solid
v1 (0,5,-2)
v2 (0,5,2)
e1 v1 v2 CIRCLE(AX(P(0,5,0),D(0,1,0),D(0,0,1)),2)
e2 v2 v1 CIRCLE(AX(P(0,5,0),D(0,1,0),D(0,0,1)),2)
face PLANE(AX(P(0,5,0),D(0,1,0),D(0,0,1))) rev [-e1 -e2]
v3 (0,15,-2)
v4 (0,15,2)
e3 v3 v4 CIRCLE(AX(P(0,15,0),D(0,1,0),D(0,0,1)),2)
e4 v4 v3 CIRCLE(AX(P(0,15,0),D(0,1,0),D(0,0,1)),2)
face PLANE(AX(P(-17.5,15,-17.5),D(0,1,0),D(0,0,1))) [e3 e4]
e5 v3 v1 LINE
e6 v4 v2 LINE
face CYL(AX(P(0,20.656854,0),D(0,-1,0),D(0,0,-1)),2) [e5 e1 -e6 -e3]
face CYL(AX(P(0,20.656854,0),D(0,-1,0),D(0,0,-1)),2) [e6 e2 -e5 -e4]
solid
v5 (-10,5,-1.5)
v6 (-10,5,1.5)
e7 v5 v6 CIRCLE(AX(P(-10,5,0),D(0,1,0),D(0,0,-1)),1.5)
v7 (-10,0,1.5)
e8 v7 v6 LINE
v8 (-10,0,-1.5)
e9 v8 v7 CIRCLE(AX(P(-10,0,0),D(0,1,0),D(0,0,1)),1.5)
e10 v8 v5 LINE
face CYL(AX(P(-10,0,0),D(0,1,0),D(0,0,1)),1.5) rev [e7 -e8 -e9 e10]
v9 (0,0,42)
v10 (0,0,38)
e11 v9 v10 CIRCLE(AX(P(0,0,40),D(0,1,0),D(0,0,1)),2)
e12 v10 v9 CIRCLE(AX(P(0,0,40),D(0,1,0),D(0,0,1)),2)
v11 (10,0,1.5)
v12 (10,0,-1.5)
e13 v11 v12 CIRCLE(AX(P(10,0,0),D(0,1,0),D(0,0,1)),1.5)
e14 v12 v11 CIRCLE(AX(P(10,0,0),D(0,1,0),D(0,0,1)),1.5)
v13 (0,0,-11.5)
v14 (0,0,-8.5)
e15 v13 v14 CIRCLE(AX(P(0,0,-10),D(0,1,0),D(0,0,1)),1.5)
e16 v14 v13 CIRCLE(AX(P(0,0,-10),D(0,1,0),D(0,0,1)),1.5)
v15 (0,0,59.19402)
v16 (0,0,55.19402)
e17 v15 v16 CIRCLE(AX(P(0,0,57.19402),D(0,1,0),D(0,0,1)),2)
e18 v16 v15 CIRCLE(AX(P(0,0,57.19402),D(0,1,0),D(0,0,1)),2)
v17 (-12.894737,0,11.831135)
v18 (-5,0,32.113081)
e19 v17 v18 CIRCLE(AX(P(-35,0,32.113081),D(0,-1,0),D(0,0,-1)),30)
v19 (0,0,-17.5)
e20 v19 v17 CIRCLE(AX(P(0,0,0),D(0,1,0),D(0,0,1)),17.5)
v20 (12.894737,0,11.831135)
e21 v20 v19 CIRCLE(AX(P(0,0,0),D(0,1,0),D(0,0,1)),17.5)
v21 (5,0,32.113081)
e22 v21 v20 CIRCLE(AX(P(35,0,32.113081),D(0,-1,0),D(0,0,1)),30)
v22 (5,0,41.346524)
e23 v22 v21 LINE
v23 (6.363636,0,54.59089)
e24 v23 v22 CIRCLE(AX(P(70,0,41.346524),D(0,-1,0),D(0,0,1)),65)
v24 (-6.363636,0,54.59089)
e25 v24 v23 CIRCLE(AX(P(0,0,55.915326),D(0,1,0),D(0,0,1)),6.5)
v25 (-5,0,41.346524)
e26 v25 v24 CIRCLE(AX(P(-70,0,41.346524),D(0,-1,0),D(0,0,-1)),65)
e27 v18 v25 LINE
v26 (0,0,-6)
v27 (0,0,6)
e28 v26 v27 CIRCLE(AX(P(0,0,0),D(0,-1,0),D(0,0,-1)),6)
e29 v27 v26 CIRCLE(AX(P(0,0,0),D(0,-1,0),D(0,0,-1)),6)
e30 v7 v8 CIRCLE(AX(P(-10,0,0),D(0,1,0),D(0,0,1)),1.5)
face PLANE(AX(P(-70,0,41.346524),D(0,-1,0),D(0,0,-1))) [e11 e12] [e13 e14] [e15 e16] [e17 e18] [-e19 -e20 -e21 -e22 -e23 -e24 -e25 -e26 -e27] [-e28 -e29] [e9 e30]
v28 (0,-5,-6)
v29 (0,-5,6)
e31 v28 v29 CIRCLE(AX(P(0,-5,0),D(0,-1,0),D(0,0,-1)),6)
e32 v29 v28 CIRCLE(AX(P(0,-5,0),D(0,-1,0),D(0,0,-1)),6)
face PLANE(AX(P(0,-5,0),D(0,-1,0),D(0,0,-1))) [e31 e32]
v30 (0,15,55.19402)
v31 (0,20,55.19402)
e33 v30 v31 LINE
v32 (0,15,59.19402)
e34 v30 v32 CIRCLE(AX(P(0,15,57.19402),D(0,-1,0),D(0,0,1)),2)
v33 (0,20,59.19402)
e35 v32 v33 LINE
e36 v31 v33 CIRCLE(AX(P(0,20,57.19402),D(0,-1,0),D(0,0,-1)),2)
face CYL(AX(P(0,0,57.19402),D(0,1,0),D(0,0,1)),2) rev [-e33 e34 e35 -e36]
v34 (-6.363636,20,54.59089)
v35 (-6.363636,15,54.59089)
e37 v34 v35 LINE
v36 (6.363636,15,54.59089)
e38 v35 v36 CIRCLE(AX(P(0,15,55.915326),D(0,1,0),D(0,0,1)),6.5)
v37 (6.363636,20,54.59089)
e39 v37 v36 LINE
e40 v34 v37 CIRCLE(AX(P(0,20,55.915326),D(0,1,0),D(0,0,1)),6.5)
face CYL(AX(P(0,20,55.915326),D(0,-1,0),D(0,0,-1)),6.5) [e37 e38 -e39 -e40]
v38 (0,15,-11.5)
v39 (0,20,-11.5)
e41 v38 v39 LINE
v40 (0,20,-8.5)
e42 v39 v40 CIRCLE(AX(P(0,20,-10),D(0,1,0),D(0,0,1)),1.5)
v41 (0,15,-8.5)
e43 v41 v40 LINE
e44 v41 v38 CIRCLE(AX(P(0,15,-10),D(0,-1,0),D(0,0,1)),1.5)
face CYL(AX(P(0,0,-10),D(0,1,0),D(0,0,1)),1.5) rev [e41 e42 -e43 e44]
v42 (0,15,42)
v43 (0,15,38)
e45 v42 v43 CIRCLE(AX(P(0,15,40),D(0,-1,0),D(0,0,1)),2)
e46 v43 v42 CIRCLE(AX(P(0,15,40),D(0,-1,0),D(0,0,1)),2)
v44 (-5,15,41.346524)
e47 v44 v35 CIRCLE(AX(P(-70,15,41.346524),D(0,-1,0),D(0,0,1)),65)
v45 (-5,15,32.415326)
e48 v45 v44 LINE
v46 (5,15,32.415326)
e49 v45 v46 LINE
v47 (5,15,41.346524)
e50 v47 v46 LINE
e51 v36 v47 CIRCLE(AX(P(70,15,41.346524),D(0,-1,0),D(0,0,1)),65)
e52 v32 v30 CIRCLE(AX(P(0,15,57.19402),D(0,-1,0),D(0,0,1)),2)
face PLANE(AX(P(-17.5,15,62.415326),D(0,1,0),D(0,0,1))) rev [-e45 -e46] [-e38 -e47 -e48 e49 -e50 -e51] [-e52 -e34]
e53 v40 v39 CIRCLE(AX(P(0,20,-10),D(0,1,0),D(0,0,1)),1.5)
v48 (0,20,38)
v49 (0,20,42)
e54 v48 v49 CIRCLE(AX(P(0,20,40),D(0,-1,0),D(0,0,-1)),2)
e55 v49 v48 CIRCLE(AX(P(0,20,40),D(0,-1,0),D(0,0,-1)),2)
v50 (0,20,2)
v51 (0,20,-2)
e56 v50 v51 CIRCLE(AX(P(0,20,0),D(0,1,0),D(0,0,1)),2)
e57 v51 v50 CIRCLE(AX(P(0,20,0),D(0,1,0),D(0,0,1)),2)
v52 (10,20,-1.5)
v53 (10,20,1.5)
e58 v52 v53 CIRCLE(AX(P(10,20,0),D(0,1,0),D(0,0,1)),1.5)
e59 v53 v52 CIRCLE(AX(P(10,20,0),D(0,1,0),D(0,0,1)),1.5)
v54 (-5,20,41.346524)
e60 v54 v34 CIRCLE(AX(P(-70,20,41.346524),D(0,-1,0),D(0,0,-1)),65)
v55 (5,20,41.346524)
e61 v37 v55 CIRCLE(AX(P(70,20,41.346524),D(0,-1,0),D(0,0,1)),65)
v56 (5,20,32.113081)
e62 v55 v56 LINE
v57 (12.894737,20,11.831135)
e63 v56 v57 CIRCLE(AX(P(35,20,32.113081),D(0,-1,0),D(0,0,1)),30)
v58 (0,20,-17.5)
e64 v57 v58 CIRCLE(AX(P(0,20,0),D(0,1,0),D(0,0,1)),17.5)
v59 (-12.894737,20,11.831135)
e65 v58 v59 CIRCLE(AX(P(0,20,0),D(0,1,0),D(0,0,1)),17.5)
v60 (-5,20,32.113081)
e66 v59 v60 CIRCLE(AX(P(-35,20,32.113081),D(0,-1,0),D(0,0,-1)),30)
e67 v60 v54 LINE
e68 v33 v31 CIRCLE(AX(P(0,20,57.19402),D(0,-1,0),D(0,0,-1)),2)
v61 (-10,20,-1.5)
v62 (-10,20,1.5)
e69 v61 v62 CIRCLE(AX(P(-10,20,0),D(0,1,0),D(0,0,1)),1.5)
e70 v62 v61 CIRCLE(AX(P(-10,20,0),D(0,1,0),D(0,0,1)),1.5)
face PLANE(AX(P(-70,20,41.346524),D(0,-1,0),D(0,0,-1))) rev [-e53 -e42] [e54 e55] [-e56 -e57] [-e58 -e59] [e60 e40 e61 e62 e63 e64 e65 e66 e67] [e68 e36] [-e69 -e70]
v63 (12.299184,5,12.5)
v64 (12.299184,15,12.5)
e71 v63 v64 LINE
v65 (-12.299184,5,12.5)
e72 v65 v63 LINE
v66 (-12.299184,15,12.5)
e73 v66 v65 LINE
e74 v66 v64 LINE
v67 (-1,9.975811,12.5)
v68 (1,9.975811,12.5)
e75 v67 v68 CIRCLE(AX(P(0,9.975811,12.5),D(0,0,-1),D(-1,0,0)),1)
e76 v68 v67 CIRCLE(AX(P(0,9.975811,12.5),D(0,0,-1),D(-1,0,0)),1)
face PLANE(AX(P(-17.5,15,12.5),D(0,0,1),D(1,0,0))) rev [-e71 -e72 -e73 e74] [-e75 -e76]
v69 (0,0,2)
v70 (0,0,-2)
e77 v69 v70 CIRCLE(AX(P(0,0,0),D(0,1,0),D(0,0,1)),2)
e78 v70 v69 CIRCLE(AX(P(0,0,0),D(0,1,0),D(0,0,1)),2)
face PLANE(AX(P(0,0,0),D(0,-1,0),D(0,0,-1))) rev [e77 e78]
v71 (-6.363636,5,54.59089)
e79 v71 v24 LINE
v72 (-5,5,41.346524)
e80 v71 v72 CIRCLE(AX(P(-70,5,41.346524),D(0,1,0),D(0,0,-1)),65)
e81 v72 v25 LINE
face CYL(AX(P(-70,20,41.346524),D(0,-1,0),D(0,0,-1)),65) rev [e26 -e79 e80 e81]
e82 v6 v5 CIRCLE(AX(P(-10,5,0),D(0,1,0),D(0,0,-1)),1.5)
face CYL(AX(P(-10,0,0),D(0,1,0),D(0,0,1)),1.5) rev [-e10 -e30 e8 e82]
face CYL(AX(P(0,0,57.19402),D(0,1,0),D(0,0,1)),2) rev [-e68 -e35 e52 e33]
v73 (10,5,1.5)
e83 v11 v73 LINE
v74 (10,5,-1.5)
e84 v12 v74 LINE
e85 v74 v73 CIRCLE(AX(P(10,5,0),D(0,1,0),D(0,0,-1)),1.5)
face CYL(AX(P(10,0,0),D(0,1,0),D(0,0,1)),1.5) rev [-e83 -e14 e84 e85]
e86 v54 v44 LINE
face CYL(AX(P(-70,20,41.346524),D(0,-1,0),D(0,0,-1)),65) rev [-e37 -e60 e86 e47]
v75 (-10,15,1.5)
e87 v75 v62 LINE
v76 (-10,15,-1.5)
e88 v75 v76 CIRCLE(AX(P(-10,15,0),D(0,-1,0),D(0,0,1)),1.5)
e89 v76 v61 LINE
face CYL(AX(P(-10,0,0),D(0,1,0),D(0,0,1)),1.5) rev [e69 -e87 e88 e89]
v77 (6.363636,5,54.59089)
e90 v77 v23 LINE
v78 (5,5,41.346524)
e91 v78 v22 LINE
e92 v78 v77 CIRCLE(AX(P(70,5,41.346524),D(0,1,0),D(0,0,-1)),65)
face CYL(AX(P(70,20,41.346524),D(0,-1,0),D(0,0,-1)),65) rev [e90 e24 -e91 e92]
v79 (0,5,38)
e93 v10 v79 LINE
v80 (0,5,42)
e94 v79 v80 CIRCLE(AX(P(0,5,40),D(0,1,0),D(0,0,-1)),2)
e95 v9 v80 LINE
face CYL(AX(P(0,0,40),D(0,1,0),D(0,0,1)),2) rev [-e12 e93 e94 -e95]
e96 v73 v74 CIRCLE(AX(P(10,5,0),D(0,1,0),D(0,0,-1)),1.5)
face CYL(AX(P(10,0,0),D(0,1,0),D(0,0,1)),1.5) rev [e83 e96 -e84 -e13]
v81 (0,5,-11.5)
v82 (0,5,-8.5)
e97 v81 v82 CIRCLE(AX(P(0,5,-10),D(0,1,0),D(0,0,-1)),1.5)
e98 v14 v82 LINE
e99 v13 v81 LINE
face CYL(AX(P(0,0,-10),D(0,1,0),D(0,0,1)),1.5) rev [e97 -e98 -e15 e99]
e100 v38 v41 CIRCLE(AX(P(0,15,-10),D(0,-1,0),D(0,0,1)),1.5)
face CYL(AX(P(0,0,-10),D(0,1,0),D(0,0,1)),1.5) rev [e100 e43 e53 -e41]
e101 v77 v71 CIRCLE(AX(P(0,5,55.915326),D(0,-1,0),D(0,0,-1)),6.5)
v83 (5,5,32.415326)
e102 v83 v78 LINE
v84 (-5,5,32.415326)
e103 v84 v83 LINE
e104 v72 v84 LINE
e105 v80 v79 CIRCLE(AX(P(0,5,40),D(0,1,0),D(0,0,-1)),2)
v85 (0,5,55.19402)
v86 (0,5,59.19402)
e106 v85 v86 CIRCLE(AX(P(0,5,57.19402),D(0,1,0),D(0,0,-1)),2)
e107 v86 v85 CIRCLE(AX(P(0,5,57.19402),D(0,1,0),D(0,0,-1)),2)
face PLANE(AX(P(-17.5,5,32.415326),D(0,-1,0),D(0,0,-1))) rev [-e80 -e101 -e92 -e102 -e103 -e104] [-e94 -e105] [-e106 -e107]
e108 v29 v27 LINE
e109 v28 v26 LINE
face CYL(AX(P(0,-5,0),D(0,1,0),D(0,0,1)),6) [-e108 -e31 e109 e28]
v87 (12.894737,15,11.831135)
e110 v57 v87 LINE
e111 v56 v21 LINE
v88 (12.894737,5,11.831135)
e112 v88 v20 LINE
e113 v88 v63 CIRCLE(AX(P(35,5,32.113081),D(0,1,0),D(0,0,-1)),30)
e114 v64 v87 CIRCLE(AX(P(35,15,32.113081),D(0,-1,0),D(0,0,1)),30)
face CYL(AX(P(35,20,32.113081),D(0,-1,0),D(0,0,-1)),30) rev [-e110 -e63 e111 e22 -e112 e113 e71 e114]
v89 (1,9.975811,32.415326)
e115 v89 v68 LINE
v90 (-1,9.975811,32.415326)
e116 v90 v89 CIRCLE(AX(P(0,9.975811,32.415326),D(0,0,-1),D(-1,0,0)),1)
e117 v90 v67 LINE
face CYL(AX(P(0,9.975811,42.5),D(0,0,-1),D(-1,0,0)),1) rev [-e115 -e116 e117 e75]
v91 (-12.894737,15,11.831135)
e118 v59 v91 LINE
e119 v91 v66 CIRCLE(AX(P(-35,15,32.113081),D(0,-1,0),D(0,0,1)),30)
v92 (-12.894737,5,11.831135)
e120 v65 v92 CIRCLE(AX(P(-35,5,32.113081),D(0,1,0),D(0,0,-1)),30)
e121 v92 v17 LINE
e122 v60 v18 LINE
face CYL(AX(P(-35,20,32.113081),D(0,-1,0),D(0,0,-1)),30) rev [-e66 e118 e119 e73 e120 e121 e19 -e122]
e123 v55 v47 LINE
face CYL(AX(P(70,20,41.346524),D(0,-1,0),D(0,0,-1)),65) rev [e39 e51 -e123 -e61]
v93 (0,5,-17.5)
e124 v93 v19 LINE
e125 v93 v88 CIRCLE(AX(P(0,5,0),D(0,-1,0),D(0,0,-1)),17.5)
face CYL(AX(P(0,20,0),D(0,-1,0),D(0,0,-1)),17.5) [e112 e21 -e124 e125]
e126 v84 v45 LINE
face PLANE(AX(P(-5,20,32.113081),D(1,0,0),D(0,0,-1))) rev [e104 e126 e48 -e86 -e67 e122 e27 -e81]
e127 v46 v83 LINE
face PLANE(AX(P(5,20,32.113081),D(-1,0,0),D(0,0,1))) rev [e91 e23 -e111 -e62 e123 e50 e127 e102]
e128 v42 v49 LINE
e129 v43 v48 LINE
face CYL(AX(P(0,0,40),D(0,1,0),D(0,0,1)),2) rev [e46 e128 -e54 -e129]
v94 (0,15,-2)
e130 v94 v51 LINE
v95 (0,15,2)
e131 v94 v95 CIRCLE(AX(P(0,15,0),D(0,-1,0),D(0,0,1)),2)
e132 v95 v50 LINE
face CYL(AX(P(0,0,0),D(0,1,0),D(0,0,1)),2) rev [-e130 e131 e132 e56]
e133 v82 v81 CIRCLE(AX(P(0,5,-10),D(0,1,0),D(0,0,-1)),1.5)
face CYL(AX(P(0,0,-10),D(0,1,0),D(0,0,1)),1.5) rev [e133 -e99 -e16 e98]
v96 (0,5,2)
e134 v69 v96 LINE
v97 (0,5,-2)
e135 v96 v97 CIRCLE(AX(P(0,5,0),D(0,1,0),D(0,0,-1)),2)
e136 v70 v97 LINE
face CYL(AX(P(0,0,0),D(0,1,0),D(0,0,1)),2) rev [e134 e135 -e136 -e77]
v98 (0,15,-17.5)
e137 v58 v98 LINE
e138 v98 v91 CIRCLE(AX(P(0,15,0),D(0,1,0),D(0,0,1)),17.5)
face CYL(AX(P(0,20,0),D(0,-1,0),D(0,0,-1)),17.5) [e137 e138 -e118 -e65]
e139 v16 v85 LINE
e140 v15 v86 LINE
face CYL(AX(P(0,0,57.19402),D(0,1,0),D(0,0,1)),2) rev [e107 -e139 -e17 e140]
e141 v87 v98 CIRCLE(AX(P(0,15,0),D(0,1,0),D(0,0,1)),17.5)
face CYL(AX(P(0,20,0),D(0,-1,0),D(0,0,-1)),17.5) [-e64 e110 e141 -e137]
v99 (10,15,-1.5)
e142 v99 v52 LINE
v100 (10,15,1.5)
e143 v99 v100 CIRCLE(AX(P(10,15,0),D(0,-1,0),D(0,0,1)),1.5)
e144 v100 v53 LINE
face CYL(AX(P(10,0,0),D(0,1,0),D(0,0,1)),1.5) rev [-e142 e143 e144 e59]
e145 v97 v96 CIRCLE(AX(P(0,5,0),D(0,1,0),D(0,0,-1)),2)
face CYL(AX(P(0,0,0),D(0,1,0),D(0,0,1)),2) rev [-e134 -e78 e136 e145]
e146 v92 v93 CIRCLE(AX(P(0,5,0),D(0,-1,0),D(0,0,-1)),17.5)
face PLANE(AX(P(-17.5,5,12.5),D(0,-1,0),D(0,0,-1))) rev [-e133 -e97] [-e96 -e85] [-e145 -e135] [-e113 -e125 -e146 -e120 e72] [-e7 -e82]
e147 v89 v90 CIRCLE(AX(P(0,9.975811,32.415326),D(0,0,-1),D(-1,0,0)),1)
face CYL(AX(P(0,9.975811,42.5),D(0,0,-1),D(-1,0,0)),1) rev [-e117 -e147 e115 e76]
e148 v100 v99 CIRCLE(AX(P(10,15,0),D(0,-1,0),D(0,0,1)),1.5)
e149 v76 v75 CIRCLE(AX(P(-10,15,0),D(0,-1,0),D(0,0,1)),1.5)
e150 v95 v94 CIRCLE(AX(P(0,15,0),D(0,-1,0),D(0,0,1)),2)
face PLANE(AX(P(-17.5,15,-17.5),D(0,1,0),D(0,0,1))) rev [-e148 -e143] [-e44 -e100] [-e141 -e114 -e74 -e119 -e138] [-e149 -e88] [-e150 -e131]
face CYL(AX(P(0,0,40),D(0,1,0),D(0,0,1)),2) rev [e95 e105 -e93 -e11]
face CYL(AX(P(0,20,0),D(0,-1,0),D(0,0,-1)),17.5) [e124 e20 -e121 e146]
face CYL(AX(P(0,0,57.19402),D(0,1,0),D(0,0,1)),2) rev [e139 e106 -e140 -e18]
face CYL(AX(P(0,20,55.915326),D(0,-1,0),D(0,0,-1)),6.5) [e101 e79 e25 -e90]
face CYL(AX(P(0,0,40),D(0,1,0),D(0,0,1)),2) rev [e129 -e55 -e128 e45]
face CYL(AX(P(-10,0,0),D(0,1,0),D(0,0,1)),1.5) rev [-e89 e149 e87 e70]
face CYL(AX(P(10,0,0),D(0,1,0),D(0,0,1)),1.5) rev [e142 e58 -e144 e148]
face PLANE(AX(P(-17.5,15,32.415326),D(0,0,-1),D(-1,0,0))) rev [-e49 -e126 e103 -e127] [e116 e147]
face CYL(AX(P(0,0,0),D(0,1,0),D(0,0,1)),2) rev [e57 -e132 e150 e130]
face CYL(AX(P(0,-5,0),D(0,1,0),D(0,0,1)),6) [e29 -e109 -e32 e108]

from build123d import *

# Parameters (mm, degrees)
BOSS_EXTRUDE1_DEPTH     = 20
CUT_EXTRUDE1_DEPTH      = 68.837474407
CUT_EXTRUDE1_DEPTH_BACK = 68.837474407
SKETCH2_R               = 2
SKETCH3_R               = 2
CUT_EXTRUDE2_DEPTH      = 68.837474407
SKETCH4_R               = 1.5
CUT_EXTRUDE3_DEPTH      = 68.837474407
CUT_EXTRUDE4_DEPTH      = 68.837474407
CUT_EXTRUDE4_DEPTH_BACK = 68.837474407
SKETCH5_W               = 30
SKETCH5_H               = 10
SKETCH6_R               = 6
BOSS_EXTRUDE2_DEPTH     = 5
SKETCH7_R               = 2
BOSS_EXTRUDE4_DEPTH     = 10
SKETCH8_R               = 1
CUT_EXTRUDE5_DEPTH      = 30


with BuildPart() as part:
    # Sketch1 → Boss-Extrude1 (new body)
    with BuildSketch(Plane(origin=(0, 0, 0), x_dir=(1, 0, 0), z_dir=(0, 1, 0))):
        with BuildLine():
            Line((-5, -32.113081447), (-5, -41.34652383))
            ThreePointArc((-5, -41.34652383), (-5.341807803, -48.003714064), (-6.363636364, -54.590889543))
            ThreePointArc((-6.363636364, -54.590889543), (0, -62.415326114), (6.363636364, -54.590889543))
            ThreePointArc((6.363636364, -54.590889543), (5.341807803, -48.003714064), (5, -41.34652383))
            Line((5, -41.34652383), (5, -32.113081447))
            ThreePointArc((5, -32.113081447), (7.043266511, -21.230937695), (12.894736842, -11.83113527))
            ThreePointArc((12.894736842, -11.83113527), (0, 17.5), (-12.894736842, -11.83113527))
            ThreePointArc((-12.894736842, -11.83113527), (-7.043266511, -21.230937695), (-5, -32.113081447))
        make_face()
    extrude(amount=BOSS_EXTRUDE1_DEPTH)

    # Sketch2 → Cut-Extrude1 (cut, two sides: drawn at the far end of the back side and taken through both)
    with BuildSketch(Plane(origin=(0, 20, 0), x_dir=(1, 0, 0), z_dir=(0, 1, 0)).offset(-CUT_EXTRUDE1_DEPTH_BACK)):
        with Locations(Location((0, -40, 0), (0, 0, 270))):
            Circle(SKETCH2_R)
        with Locations(Location((0, -57.194020253, 0), (0, 0, 270))):
            Circle(SKETCH2_R)
    extrude(amount=CUT_EXTRUDE1_DEPTH + CUT_EXTRUDE1_DEPTH_BACK, mode=Mode.SUBTRACT)

    # Sketch3 → Cut-Extrude2 (cut, through all)
    with BuildSketch(Plane(origin=(0, 20, 0), x_dir=(1, 0, 0), z_dir=(0, 1, 0))):
        with Locations(Location((0, 0, 0), (0, 0, 270))):
            Circle(SKETCH3_R)
    extrude(amount=-CUT_EXTRUDE2_DEPTH, mode=Mode.SUBTRACT)

    # Sketch4 → Cut-Extrude3 (cut, through all)
    with BuildSketch(Plane(origin=(0, 20, 0), x_dir=(1, 0, 0), z_dir=(0, 1, 0))):
        with Locations(Location((-10, 0, 0), (0, 0, 270))):
            Circle(SKETCH4_R)
        with Locations(Location((10, 0, 0), (0, 0, 270))):
            Circle(SKETCH4_R)
        with Locations(Location((0, 10, 0), (0, 0, 270))):
            Circle(SKETCH4_R)
    extrude(amount=-CUT_EXTRUDE3_DEPTH, mode=Mode.SUBTRACT)

    # Sketch5 → Cut-Extrude4 (cut, two sides: drawn at the far end of the back side and taken through both)
    with BuildSketch(Plane(origin=(0, 0, 0), x_dir=(0, 0, -1), z_dir=(1, 0, 0)).offset(-CUT_EXTRUDE4_DEPTH_BACK)):
        with Locations((-47.415326114, 10)):
            Rectangle(SKETCH5_W, SKETCH5_H)
        with Locations((2.5, 10)):
            Rectangle(SKETCH5_W, SKETCH5_H)
    extrude(amount=CUT_EXTRUDE4_DEPTH + CUT_EXTRUDE4_DEPTH_BACK, mode=Mode.SUBTRACT)

    # Sketch6 → Boss-Extrude2 (add)
    with BuildSketch(Plane.XZ):
        with Locations(Location((0, 0, 0), (0, 0, 270))):
            Circle(SKETCH6_R)
    extrude(amount=BOSS_EXTRUDE2_DEPTH)

    # Sketch8 → Cut-Extrude5 (cut)
    with BuildSketch(Plane(origin=(0, 0, 12.5), x_dir=(-1, 0, 0), z_dir=(0, 0, -1))):
        with Locations((0, 9.975810979)):
            Circle(SKETCH8_R)
    extrude(amount=-CUT_EXTRUDE5_DEPTH, mode=Mode.SUBTRACT)


with BuildPart() as body_2:
    # Sketch7 → Boss-Extrude4 (new body)
    with BuildSketch(Plane(origin=(0, 5, 0), x_dir=(1, 0, 0), z_dir=(0, 1, 0))):
        with Locations(Location((0, 0, 0), (0, 0, 270))):
            Circle(SKETCH7_R)
    extrude(amount=BOSS_EXTRUDE4_DEPTH)


solid = Compound([part.part, body_2.part])
